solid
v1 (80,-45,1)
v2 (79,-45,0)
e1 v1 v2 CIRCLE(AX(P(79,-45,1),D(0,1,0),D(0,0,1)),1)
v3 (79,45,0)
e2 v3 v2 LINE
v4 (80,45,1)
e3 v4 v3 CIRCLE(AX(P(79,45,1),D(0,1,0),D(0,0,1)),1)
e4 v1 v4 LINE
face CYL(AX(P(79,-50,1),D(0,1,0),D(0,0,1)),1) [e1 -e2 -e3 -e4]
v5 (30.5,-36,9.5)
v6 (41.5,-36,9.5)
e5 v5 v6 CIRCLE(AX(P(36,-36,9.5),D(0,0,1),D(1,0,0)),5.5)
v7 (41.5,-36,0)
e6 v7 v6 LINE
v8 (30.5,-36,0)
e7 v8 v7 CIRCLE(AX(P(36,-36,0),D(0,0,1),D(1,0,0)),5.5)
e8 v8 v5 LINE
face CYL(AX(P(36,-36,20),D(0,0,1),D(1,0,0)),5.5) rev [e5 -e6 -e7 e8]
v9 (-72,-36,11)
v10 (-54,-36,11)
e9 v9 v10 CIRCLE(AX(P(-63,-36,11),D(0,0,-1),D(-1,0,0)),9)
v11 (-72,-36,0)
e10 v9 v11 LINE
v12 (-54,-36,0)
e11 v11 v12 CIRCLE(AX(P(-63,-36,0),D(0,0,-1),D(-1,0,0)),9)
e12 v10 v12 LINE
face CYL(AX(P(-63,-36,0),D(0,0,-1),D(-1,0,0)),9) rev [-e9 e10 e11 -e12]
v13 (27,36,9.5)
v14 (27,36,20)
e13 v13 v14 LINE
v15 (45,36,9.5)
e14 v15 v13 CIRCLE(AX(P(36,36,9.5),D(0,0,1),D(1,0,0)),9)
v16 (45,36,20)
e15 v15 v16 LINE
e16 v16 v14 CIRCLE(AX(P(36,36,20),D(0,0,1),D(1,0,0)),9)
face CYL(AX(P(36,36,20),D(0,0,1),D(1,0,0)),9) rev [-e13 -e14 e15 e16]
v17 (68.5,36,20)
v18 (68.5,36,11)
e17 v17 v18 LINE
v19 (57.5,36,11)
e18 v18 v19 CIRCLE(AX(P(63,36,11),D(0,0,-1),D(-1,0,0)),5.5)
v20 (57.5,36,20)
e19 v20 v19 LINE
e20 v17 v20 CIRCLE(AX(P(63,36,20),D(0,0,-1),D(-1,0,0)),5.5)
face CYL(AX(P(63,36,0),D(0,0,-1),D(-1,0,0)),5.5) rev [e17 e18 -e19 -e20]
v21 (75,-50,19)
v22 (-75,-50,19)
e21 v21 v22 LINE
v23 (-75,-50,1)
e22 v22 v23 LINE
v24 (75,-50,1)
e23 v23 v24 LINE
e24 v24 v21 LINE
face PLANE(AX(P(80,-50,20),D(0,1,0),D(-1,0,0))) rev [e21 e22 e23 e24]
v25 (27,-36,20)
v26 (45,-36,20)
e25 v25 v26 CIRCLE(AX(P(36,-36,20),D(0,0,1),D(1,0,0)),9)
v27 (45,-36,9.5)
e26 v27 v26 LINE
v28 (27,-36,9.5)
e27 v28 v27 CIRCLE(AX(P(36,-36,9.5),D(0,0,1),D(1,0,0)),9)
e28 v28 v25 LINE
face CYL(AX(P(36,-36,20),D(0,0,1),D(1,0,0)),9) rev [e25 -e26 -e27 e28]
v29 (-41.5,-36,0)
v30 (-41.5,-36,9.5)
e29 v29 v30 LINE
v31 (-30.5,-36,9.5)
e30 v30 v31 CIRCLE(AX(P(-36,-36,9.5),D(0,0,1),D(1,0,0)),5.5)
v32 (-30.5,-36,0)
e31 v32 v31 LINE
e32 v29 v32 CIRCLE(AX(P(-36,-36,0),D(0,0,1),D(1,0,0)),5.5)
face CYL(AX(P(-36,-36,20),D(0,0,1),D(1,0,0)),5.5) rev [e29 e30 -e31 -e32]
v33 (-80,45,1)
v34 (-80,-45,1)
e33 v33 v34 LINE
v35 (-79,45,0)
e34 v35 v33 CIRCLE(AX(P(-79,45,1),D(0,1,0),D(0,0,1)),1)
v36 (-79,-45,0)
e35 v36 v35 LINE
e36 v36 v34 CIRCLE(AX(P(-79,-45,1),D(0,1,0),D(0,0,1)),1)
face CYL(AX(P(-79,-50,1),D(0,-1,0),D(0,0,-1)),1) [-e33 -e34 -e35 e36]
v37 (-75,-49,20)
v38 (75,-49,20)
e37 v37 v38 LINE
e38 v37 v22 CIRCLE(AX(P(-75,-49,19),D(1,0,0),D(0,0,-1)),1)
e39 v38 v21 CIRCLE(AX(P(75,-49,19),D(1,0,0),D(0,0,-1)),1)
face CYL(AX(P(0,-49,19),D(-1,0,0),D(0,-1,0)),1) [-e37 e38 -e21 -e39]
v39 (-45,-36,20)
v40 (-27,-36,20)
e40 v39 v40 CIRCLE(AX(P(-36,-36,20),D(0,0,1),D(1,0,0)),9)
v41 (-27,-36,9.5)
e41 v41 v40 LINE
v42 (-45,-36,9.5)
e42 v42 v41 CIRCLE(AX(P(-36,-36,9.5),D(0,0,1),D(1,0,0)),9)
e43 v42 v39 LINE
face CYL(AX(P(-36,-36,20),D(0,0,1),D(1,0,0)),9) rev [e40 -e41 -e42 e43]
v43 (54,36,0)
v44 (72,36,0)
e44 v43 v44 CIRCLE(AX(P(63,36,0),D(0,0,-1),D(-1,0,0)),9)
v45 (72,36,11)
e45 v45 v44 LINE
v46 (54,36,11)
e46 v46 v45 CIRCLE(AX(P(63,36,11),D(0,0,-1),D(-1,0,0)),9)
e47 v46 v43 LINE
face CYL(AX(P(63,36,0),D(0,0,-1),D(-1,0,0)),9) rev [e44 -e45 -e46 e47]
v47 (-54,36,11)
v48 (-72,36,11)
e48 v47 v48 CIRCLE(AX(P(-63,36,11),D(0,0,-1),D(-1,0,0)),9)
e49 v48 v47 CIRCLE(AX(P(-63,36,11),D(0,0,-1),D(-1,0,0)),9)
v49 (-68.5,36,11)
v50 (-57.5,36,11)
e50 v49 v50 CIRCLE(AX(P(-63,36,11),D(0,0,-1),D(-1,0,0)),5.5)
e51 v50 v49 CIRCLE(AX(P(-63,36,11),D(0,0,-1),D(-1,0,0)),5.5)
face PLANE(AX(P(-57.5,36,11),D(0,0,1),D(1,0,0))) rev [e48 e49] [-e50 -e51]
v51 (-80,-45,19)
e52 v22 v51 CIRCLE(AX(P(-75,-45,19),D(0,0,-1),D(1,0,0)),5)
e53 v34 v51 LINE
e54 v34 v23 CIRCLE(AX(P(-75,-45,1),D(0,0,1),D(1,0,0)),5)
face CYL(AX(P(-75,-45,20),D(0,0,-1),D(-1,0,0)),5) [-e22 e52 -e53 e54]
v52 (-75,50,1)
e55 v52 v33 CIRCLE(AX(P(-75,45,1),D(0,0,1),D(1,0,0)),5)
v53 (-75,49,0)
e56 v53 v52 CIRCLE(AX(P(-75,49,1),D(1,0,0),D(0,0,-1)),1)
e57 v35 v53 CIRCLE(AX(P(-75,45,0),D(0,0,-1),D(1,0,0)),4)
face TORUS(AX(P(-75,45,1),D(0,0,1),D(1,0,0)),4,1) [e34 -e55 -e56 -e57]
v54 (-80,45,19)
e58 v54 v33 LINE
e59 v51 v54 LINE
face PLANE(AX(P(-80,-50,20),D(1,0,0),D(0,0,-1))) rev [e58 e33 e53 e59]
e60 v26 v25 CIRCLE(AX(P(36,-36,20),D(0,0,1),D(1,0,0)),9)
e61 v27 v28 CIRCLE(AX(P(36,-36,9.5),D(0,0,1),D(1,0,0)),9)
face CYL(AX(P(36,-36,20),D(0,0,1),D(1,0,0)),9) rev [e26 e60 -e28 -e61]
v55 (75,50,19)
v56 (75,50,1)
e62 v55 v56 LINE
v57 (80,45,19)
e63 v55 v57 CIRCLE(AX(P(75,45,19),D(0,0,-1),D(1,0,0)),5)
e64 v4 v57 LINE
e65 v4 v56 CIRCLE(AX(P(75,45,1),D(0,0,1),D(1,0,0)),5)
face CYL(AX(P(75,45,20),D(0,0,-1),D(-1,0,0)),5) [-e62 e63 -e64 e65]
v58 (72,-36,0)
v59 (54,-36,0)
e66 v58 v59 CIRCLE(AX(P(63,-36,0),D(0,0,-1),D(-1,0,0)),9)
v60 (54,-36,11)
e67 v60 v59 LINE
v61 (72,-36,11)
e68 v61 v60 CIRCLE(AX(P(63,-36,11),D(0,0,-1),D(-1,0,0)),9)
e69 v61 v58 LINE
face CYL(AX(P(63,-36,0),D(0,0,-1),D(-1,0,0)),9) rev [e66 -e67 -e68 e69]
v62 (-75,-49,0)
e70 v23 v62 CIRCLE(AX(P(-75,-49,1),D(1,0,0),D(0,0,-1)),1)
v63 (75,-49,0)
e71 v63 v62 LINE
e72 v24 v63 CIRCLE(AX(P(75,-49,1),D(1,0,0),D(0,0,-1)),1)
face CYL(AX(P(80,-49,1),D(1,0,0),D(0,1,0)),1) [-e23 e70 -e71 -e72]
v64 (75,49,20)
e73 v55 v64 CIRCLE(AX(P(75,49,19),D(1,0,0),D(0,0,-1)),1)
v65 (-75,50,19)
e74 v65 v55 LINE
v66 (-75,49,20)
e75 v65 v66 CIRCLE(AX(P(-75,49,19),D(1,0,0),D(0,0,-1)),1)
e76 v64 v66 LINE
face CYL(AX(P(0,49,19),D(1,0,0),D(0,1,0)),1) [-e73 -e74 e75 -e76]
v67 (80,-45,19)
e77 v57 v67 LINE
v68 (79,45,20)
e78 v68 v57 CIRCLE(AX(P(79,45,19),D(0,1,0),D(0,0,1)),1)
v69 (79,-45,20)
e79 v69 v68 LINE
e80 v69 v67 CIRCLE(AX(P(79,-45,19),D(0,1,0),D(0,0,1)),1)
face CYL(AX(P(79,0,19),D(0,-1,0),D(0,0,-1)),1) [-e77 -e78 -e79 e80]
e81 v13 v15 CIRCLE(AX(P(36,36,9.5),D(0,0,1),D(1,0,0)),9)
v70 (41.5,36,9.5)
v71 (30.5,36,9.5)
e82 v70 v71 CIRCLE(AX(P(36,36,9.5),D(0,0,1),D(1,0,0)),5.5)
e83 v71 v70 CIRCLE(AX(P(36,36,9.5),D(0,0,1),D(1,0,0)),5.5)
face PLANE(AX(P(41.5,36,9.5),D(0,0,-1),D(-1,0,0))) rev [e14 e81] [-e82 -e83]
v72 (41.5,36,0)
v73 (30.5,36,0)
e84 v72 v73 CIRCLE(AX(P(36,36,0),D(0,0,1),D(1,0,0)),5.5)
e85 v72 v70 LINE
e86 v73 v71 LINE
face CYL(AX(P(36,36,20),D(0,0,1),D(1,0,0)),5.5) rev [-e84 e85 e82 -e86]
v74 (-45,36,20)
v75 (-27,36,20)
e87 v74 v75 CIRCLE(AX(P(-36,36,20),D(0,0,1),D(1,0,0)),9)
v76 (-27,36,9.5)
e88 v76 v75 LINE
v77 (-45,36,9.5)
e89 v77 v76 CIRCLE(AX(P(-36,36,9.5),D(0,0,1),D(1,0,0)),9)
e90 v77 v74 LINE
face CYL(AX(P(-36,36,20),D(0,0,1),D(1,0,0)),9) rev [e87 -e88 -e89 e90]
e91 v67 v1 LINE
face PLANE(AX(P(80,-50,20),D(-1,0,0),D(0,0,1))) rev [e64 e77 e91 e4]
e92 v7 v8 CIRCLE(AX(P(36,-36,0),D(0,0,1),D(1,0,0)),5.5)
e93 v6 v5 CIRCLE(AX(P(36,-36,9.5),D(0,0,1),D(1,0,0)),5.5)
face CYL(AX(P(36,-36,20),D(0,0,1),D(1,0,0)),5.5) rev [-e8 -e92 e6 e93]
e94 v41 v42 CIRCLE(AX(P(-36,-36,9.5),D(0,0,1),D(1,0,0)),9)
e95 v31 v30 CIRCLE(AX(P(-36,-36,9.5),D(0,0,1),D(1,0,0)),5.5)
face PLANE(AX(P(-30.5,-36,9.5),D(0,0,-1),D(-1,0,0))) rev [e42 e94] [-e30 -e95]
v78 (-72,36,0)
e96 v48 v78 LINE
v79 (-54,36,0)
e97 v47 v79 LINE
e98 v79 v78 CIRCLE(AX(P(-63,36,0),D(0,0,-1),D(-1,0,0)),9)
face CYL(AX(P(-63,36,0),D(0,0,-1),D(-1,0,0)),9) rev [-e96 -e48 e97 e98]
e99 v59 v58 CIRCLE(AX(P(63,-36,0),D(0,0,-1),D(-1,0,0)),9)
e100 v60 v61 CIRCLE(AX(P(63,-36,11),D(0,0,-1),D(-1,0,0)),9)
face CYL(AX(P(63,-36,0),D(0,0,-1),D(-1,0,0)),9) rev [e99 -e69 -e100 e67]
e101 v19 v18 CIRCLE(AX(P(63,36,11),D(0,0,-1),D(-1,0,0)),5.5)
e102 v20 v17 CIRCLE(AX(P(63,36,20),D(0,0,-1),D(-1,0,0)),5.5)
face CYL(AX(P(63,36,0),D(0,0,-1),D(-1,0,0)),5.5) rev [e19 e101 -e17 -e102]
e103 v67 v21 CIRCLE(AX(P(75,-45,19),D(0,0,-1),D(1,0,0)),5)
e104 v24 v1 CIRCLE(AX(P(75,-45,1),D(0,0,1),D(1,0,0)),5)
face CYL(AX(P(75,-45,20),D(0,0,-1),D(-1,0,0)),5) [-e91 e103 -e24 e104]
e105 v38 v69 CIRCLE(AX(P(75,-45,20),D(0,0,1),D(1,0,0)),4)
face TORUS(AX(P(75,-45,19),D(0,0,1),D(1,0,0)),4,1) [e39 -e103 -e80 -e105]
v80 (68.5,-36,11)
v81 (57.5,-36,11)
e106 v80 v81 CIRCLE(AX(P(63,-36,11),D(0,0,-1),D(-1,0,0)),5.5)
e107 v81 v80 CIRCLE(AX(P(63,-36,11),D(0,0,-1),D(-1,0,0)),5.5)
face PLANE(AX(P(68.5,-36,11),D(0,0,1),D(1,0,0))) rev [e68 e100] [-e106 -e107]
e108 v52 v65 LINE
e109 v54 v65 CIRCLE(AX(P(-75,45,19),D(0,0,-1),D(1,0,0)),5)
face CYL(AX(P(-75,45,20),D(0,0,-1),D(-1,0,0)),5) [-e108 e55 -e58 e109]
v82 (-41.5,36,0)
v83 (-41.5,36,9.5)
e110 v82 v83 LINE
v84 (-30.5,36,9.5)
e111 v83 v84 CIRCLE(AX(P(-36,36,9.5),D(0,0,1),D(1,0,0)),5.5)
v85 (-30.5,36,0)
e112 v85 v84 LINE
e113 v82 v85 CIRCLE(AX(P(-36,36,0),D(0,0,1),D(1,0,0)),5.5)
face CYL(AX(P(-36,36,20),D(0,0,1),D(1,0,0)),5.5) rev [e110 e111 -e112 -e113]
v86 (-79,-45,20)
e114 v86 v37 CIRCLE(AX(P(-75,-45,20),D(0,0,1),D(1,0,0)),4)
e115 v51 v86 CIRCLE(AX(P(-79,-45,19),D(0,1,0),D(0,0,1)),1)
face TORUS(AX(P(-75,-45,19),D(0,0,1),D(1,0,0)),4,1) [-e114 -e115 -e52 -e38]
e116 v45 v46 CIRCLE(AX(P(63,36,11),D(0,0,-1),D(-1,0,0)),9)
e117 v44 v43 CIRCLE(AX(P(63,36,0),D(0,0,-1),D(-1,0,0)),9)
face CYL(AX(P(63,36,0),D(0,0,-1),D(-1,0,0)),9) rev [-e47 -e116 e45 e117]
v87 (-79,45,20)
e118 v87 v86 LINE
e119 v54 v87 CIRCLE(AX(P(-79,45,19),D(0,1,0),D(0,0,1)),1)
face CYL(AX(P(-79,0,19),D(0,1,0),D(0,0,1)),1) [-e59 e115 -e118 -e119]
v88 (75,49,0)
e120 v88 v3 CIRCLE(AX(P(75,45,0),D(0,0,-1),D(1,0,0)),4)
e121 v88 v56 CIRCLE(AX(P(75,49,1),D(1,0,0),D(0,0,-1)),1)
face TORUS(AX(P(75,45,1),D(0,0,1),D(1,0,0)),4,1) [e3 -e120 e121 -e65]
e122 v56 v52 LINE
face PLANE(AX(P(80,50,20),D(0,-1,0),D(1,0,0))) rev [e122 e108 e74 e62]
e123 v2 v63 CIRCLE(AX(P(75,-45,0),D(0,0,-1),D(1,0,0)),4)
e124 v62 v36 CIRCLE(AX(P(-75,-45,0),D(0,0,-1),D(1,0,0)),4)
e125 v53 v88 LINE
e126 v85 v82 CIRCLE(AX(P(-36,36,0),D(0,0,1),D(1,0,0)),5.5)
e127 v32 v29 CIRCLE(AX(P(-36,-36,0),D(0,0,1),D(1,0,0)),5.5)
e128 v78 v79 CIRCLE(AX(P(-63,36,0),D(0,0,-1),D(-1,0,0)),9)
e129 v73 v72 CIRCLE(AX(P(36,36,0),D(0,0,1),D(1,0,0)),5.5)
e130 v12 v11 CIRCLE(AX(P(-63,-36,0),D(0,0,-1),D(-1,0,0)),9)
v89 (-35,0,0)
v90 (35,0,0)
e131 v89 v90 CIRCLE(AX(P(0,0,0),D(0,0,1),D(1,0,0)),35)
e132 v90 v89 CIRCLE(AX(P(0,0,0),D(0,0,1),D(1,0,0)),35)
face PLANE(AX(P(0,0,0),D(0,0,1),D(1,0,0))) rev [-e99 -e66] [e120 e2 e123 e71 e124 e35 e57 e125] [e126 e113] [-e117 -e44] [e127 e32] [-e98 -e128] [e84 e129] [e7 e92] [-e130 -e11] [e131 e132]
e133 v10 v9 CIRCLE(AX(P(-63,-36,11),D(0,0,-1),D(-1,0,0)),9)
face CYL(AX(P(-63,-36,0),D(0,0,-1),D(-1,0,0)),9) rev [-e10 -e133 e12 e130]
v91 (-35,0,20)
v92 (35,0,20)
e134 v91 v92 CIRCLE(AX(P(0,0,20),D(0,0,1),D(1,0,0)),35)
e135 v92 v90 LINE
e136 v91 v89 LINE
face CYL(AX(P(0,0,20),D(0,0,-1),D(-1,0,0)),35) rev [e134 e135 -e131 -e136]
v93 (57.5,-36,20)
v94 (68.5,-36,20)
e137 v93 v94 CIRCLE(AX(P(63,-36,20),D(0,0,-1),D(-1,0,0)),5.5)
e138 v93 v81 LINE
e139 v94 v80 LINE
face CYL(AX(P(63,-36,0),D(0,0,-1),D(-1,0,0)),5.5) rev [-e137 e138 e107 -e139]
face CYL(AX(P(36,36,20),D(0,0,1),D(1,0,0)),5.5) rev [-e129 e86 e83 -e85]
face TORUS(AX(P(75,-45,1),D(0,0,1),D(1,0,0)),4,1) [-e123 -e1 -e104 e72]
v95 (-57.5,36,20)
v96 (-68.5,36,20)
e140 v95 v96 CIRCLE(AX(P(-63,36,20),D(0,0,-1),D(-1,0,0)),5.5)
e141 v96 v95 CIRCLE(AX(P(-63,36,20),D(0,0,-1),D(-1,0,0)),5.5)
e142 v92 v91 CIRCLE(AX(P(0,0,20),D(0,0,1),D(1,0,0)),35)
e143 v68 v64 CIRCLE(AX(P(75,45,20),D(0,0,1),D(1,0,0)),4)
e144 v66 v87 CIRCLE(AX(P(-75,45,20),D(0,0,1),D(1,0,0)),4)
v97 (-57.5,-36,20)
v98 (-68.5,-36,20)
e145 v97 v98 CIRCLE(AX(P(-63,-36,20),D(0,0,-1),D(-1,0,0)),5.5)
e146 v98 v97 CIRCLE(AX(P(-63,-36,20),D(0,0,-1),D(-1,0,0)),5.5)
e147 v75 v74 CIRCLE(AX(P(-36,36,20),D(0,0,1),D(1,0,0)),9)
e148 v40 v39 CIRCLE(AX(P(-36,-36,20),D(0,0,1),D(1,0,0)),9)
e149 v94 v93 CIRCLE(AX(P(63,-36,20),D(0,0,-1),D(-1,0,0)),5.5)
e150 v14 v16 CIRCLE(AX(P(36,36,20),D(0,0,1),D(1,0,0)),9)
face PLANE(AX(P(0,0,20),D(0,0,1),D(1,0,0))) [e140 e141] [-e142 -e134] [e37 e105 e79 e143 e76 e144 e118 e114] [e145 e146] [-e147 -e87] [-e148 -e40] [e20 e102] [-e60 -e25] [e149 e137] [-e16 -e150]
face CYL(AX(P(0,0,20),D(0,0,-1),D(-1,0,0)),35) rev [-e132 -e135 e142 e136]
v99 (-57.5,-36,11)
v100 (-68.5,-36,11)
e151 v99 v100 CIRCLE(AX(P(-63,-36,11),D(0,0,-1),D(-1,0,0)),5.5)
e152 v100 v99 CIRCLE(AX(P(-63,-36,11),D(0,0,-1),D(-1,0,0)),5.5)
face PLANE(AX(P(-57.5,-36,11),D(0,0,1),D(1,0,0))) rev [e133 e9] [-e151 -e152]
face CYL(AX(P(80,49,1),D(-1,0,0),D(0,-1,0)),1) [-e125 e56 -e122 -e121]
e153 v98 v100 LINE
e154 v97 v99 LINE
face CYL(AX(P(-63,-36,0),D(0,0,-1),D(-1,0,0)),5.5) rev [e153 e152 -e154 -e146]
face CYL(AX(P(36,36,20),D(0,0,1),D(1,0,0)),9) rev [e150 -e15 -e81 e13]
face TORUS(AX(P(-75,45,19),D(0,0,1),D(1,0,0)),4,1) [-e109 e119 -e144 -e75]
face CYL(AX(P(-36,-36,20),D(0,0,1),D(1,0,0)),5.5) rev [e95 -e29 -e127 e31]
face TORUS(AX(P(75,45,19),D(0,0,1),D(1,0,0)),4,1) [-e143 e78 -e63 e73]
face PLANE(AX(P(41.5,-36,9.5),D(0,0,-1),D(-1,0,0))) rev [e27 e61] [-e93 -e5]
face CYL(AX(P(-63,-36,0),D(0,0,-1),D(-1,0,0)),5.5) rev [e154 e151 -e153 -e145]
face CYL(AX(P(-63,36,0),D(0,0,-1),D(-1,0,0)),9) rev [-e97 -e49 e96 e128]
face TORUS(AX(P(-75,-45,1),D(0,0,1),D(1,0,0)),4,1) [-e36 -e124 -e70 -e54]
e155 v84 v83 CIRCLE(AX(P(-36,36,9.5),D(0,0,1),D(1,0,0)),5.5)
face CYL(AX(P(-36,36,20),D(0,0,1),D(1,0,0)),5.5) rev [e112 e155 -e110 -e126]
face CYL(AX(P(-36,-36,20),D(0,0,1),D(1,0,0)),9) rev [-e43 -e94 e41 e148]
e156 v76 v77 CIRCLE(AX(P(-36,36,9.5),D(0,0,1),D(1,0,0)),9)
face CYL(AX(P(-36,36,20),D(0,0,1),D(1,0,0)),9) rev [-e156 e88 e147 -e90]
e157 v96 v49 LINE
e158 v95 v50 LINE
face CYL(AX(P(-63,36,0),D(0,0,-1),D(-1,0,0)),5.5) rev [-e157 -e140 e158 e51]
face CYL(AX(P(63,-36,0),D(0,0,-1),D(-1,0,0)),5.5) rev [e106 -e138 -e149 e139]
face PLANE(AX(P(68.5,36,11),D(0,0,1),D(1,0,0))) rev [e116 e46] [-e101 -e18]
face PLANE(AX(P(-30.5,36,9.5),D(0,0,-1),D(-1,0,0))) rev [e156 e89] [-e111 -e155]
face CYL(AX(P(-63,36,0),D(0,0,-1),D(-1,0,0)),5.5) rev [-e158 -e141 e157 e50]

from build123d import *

# Parameters (mm, degrees)
SKETCH1_W                                           = 160
SKETCH1_H                                           = 100
SKETCH1_R                                           = 35
BOSS_EXTRUDE1_DEPTH                                 = 20
FILLET1_R                                           = 5
HOLE_SPEC_PER_SOCKET_HEAD_CAP_SCREW_TYP_D           = 11
HOLE_SPEC_PER_SOCKET_HEAD_CAP_SCREW_TYP_CBORE_D     = 18
HOLE_SPEC_PER_SOCKET_HEAD_CAP_SCREW_TYP_CBORE_DEPTH = 10.5
HOLE_SPEC_PER_SOCKET_HEAD_CAP_SCREW_2_D             = 11
HOLE_SPEC_PER_SOCKET_HEAD_CAP_SCREW_2_CBORE_D       = 18
HOLE_SPEC_PER_SOCKET_HEAD_CAP_SCREW_2_CBORE_DEPTH   = 11
FILLET2_R                                           = 1


with BuildPart() as part:
    # Sketch1 → Boss-Extrude1 (new body)
    with BuildSketch(Plane.XY):
        Rectangle(SKETCH1_W, SKETCH1_H)
        Circle(SKETCH1_R, mode=Mode.SUBTRACT)
    extrude(amount=BOSS_EXTRUDE1_DEPTH)

    # Fillet1
    fillet1_edges = [part.edges().sort_by_distance(p)[0] for p in [
        (-80, 50, 10),
        (80, 50, 10),
        (80, -50, 10),
        (-80, -50, 10),
    ]]
    fillet(fillet1_edges, radius=FILLET1_R)

    # Hole Spec _per socket head cap screw typ (through all)
    with Locations(Plane.XY.offset(20)):
        with Locations((-36, 36), (36, 36), (-36, -36), (36, -36)):
            CounterBoreHole(HOLE_SPEC_PER_SOCKET_HEAD_CAP_SCREW_TYP_D / 2, HOLE_SPEC_PER_SOCKET_HEAD_CAP_SCREW_TYP_CBORE_D / 2, HOLE_SPEC_PER_SOCKET_HEAD_CAP_SCREW_TYP_CBORE_DEPTH)

    # Hole Spec _per socket head cap screw 2 (through all)
    with Locations(Plane(origin=(0, 0, 0), x_dir=(-1, 0, 0), z_dir=(0, 0, -1))):
        with Locations((-63, 36), (63, 36), (-63, -36), (63, -36)):
            CounterBoreHole(HOLE_SPEC_PER_SOCKET_HEAD_CAP_SCREW_2_D / 2, HOLE_SPEC_PER_SOCKET_HEAD_CAP_SCREW_2_CBORE_D / 2, HOLE_SPEC_PER_SOCKET_HEAD_CAP_SCREW_2_CBORE_DEPTH)

    # Fillet2
    fillet2_edges = [part.edges().sort_by_distance(p)[0] for p in [
        (80, 0, 0),
        (80, 0, 20),
        (-80, 0, 0),
        (0, 50, 0),
        (0, -50, 0),
        (78.535533906, 48.535533906, 0),
        (-78.535533906, 48.535533906, 0),
        (-78.535533906, -48.535533906, 0),
        (78.535533906, -48.535533906, 0),
        (0, -50, 20),
        (-80, 0, 20),
        (0, 50, 20),
        (78.535533906, 48.535533906, 20),
        (-78.535533906, 48.535533906, 20),
        (-78.535533906, -48.535533906, 20),
        (78.535533906, -48.535533906, 20),
    ]]
    fillet(fillet2_edges, radius=FILLET2_R)


solid = part.part
